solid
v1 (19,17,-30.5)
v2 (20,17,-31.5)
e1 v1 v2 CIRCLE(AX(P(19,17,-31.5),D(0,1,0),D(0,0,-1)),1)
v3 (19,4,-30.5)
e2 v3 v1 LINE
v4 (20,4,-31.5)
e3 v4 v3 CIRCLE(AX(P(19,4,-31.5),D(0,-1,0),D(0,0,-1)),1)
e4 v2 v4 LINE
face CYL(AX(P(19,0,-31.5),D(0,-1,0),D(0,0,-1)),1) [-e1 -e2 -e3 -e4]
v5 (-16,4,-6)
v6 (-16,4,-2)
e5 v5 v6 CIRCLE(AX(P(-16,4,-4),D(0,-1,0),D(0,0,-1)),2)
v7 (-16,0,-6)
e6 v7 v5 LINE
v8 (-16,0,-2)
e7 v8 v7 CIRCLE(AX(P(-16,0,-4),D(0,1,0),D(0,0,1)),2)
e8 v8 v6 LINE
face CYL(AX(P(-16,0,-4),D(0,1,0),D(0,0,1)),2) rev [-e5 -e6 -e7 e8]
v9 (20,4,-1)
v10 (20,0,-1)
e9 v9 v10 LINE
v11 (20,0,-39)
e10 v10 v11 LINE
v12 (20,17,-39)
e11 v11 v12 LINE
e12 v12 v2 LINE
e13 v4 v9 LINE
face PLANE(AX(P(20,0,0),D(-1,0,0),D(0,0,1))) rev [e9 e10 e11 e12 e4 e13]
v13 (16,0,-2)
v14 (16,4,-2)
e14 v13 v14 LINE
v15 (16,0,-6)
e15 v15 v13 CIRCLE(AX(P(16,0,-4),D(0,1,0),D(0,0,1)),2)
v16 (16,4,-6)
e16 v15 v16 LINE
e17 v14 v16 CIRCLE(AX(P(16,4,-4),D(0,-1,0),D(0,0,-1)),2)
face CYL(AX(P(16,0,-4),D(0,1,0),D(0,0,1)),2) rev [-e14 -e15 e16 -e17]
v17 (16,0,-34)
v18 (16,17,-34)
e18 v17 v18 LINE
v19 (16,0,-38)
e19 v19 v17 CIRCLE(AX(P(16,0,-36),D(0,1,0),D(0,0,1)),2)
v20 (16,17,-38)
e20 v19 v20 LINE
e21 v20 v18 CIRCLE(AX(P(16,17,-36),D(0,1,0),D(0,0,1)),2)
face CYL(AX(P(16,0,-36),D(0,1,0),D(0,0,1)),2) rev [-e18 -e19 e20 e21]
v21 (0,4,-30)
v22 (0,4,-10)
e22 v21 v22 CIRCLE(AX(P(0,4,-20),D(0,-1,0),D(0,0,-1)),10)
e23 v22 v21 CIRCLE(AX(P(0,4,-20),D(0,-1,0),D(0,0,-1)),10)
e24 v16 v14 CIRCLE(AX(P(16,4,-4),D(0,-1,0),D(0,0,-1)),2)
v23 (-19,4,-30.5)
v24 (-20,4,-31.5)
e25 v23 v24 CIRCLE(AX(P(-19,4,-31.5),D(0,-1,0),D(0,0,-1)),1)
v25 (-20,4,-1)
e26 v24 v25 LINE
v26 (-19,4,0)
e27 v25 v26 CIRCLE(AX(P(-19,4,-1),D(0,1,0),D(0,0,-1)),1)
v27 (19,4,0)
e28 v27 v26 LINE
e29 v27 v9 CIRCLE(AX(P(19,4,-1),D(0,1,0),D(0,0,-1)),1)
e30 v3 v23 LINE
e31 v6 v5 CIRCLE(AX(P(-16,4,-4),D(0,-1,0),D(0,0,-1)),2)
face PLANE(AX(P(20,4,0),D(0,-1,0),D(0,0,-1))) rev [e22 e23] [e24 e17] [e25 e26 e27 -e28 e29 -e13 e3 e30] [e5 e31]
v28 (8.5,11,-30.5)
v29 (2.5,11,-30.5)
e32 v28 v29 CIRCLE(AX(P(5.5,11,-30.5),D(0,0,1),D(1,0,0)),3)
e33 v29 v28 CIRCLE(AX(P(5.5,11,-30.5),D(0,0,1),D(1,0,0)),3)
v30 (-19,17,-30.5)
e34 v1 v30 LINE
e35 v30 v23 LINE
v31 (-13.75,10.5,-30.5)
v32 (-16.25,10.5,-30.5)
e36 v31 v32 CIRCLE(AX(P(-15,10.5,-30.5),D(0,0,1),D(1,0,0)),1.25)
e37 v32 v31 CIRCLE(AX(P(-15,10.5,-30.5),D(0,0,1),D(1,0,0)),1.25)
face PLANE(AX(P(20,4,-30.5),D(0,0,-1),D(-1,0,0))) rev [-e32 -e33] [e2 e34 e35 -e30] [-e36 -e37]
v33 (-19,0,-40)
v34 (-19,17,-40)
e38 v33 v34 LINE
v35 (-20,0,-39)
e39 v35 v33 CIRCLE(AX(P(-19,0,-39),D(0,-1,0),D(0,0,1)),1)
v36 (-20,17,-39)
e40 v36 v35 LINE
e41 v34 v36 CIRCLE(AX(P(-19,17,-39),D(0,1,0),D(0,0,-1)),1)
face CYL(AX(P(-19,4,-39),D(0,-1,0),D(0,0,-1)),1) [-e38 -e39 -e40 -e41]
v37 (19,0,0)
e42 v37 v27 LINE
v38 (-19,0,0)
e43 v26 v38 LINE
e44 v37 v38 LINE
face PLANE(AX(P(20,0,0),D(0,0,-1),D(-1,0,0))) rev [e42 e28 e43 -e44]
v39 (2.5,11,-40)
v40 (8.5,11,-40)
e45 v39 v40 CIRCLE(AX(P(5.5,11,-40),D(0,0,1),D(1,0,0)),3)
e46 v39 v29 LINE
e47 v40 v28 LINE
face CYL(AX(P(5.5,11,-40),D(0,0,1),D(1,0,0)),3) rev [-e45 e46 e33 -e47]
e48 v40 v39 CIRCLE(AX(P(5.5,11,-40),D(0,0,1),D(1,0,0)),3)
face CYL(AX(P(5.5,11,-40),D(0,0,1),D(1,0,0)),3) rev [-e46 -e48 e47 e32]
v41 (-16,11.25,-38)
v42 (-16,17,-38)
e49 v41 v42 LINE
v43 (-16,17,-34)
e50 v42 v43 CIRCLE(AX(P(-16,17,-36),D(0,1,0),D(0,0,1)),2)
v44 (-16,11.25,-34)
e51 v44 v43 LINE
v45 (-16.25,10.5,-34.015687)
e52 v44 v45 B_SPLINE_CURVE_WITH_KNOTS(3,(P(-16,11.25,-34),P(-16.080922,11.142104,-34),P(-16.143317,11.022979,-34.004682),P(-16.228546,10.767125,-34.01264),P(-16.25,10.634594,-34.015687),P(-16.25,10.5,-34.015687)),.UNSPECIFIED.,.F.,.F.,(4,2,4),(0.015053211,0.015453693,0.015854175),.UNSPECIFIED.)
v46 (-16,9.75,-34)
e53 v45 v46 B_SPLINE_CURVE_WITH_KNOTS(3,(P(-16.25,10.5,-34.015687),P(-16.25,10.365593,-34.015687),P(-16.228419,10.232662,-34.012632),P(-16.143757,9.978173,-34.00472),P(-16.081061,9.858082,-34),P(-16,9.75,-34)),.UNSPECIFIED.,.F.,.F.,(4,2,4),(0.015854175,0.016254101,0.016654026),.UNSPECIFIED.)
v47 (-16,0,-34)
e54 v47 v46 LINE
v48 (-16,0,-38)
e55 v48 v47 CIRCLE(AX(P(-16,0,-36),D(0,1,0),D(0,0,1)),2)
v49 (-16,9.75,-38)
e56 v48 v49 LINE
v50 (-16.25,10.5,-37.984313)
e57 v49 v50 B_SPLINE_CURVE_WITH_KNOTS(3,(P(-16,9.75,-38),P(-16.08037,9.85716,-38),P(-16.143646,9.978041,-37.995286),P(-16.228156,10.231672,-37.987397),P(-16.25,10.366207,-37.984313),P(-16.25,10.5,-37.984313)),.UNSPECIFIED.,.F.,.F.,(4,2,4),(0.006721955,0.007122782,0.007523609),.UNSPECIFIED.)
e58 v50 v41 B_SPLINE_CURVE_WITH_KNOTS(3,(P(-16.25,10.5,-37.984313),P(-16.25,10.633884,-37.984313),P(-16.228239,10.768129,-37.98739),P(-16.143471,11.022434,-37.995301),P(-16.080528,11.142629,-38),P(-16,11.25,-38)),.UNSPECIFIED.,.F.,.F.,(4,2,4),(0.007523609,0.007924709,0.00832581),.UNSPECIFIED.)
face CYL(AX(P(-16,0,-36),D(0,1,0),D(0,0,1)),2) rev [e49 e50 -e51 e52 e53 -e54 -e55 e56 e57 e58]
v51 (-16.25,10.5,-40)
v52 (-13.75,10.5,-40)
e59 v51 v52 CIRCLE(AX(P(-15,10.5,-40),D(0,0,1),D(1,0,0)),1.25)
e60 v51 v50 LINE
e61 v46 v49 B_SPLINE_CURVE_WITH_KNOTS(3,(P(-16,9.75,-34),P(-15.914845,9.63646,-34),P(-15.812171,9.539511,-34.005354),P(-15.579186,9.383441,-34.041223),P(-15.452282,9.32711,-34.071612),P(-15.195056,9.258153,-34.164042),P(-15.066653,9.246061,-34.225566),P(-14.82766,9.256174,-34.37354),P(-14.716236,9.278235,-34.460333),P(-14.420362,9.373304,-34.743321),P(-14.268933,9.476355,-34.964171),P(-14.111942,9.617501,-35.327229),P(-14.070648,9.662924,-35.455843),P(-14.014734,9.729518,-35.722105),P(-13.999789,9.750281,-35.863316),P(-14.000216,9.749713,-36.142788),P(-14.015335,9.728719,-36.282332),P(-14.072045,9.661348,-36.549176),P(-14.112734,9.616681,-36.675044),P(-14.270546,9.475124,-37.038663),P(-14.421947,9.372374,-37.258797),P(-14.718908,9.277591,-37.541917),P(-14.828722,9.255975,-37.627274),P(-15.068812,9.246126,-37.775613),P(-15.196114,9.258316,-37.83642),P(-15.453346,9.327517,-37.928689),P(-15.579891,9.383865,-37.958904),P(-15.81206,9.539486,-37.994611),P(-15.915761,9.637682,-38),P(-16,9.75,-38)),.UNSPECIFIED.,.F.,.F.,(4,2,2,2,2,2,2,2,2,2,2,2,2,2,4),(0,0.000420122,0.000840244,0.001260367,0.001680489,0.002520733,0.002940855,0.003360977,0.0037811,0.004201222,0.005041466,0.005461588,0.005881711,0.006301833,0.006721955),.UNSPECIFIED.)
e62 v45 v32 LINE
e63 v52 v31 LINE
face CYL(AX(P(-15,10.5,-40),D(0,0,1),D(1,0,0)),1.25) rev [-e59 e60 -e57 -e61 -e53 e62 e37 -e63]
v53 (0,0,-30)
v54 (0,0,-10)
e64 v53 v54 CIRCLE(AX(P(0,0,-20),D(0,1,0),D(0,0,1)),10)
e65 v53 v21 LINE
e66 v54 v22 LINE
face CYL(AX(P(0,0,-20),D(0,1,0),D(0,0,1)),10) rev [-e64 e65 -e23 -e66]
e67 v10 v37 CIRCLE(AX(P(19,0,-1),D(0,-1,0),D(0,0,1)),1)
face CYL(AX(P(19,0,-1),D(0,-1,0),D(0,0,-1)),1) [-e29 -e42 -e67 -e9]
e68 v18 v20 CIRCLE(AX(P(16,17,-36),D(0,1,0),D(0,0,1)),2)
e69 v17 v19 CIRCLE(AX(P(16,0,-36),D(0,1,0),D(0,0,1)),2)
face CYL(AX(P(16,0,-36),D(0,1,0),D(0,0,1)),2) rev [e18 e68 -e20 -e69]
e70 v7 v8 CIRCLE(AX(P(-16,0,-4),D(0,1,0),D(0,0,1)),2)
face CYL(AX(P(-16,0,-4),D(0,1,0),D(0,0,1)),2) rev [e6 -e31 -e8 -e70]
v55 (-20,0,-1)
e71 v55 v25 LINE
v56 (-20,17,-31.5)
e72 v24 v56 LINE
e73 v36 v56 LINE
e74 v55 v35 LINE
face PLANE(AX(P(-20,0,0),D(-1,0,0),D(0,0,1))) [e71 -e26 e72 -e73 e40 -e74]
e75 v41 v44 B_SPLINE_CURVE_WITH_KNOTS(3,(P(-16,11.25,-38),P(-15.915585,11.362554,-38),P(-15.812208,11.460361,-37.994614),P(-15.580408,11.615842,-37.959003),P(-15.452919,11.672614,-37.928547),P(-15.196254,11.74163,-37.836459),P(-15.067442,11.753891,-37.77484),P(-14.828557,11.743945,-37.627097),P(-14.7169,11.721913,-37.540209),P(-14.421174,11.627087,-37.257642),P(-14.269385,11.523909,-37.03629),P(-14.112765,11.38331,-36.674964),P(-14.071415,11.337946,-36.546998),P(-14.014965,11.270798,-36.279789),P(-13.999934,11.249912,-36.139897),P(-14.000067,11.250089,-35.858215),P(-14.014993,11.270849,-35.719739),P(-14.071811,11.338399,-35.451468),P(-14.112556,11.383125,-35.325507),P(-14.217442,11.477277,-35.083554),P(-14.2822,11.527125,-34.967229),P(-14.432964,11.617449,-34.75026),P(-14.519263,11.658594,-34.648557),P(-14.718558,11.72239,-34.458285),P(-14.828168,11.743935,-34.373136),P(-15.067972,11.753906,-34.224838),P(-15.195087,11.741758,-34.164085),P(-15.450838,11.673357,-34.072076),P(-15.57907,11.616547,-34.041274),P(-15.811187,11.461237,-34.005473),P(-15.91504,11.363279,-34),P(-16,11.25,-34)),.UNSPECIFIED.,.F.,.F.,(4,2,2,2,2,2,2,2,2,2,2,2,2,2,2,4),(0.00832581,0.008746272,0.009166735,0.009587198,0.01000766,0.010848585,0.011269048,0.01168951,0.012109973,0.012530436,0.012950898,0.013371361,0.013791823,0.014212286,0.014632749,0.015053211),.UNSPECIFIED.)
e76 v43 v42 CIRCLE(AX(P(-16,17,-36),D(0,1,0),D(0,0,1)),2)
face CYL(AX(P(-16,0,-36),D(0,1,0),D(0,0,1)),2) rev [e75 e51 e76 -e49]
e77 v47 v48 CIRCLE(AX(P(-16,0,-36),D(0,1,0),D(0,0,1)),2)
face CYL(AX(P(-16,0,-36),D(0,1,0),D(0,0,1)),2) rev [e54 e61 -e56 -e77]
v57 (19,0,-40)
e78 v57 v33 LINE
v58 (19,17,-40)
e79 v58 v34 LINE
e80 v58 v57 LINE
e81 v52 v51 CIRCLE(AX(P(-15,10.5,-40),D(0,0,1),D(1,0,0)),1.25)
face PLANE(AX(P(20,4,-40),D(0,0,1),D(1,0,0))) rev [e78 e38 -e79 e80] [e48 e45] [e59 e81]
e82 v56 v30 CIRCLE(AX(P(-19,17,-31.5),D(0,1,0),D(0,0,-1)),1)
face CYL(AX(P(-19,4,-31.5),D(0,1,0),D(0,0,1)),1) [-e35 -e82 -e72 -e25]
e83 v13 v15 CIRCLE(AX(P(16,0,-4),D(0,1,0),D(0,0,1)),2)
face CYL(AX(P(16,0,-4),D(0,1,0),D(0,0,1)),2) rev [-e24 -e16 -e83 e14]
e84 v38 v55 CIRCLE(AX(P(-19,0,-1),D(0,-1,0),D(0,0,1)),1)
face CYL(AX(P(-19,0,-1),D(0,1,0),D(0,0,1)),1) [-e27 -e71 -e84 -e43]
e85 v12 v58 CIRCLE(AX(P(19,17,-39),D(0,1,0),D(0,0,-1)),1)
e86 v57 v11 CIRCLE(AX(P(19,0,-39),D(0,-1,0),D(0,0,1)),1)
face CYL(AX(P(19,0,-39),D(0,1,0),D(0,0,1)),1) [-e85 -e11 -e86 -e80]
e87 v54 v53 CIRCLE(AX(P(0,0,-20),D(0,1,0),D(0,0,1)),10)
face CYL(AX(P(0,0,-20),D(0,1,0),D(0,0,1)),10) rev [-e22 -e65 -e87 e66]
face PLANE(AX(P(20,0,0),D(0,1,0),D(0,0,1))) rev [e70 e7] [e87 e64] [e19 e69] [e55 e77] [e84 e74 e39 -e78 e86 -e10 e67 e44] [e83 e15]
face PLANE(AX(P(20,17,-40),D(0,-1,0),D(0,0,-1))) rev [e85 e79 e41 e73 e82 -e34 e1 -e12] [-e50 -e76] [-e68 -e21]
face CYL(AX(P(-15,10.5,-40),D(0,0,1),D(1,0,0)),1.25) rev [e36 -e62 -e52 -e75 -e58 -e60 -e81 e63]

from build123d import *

# Parameters (mm, degrees)
BOSS_EXTRUDE1_DEPTH     = 20
CUT_EXTRUDE1_DEPTH      = 47.572524089
CUT_EXTRUDE1_DEPTH_BACK = 47.572524089
SKETCH2_R               = 10
SKETCH2_R_2             = 2
FILLET1_R               = 1
SKETCH3_R               = 3
SKETCH3_R_2             = 1.25
CUT_EXTRUDE2_DEPTH      = 41.239905566


with BuildPart() as part:
    # Sketch1 → Boss-Extrude1 (new, symmetric)
    with BuildSketch(Plane(origin=(0, 0, 0), x_dir=(0, 0, -1), z_dir=(1, 0, 0))):
        Polygon((0, 0), (40, 0), (40, 4), (40, 17), (30.5, 17), (30.5, 4), (0, 4), align=None)
    extrude(amount=BOSS_EXTRUDE1_DEPTH, both=True)

    # Sketch2 → Cut-Extrude1 (cut, two sides: drawn at the far end of the back side and taken through both)
    with BuildSketch(Plane(origin=(0, 4, 0), x_dir=(1, 0, 0), z_dir=(0, 1, 0)).offset(-CUT_EXTRUDE1_DEPTH_BACK)):
        with Locations(Location((0, 20, 0), (0, 0, 270))):
            Circle(SKETCH2_R)
        with Locations(Location((16, 36, 0), (0, 0, 270))):
            Circle(SKETCH2_R_2)
        with Locations(Location((16, 4, 0), (0, 0, 270))):
            Circle(SKETCH2_R_2)
        with Locations(Location((-16, 4, 0), (0, 0, 270))):
            Circle(SKETCH2_R_2)
        with Locations(Location((-16, 36, 0), (0, 0, 270))):
            Circle(SKETCH2_R_2)
    extrude(amount=CUT_EXTRUDE1_DEPTH + CUT_EXTRUDE1_DEPTH_BACK, mode=Mode.SUBTRACT)

    # Fillet1
    fillet1_edges = [part.edges().sort_by_distance(p)[0] for p in [
        (20, 8.5, -40),
        (20, 10.5, -30.5),
        (20, 2, 0),
        (-20, 10.5, -30.5),
        (-20, 8.5, -40),
        (-20, 2, 0),
    ]]
    fillet(fillet1_edges, radius=FILLET1_R)

    # Sketch3 → Cut-Extrude2 (cut, through all)
    with BuildSketch(Plane.XY.offset(-30.5)):
        with Locations((5.5, 11)):
            Circle(SKETCH3_R)
        with Locations((-15, 10.5)):
            Circle(SKETCH3_R_2)
    extrude(amount=-CUT_EXTRUDE2_DEPTH, mode=Mode.SUBTRACT)


solid = part.part
